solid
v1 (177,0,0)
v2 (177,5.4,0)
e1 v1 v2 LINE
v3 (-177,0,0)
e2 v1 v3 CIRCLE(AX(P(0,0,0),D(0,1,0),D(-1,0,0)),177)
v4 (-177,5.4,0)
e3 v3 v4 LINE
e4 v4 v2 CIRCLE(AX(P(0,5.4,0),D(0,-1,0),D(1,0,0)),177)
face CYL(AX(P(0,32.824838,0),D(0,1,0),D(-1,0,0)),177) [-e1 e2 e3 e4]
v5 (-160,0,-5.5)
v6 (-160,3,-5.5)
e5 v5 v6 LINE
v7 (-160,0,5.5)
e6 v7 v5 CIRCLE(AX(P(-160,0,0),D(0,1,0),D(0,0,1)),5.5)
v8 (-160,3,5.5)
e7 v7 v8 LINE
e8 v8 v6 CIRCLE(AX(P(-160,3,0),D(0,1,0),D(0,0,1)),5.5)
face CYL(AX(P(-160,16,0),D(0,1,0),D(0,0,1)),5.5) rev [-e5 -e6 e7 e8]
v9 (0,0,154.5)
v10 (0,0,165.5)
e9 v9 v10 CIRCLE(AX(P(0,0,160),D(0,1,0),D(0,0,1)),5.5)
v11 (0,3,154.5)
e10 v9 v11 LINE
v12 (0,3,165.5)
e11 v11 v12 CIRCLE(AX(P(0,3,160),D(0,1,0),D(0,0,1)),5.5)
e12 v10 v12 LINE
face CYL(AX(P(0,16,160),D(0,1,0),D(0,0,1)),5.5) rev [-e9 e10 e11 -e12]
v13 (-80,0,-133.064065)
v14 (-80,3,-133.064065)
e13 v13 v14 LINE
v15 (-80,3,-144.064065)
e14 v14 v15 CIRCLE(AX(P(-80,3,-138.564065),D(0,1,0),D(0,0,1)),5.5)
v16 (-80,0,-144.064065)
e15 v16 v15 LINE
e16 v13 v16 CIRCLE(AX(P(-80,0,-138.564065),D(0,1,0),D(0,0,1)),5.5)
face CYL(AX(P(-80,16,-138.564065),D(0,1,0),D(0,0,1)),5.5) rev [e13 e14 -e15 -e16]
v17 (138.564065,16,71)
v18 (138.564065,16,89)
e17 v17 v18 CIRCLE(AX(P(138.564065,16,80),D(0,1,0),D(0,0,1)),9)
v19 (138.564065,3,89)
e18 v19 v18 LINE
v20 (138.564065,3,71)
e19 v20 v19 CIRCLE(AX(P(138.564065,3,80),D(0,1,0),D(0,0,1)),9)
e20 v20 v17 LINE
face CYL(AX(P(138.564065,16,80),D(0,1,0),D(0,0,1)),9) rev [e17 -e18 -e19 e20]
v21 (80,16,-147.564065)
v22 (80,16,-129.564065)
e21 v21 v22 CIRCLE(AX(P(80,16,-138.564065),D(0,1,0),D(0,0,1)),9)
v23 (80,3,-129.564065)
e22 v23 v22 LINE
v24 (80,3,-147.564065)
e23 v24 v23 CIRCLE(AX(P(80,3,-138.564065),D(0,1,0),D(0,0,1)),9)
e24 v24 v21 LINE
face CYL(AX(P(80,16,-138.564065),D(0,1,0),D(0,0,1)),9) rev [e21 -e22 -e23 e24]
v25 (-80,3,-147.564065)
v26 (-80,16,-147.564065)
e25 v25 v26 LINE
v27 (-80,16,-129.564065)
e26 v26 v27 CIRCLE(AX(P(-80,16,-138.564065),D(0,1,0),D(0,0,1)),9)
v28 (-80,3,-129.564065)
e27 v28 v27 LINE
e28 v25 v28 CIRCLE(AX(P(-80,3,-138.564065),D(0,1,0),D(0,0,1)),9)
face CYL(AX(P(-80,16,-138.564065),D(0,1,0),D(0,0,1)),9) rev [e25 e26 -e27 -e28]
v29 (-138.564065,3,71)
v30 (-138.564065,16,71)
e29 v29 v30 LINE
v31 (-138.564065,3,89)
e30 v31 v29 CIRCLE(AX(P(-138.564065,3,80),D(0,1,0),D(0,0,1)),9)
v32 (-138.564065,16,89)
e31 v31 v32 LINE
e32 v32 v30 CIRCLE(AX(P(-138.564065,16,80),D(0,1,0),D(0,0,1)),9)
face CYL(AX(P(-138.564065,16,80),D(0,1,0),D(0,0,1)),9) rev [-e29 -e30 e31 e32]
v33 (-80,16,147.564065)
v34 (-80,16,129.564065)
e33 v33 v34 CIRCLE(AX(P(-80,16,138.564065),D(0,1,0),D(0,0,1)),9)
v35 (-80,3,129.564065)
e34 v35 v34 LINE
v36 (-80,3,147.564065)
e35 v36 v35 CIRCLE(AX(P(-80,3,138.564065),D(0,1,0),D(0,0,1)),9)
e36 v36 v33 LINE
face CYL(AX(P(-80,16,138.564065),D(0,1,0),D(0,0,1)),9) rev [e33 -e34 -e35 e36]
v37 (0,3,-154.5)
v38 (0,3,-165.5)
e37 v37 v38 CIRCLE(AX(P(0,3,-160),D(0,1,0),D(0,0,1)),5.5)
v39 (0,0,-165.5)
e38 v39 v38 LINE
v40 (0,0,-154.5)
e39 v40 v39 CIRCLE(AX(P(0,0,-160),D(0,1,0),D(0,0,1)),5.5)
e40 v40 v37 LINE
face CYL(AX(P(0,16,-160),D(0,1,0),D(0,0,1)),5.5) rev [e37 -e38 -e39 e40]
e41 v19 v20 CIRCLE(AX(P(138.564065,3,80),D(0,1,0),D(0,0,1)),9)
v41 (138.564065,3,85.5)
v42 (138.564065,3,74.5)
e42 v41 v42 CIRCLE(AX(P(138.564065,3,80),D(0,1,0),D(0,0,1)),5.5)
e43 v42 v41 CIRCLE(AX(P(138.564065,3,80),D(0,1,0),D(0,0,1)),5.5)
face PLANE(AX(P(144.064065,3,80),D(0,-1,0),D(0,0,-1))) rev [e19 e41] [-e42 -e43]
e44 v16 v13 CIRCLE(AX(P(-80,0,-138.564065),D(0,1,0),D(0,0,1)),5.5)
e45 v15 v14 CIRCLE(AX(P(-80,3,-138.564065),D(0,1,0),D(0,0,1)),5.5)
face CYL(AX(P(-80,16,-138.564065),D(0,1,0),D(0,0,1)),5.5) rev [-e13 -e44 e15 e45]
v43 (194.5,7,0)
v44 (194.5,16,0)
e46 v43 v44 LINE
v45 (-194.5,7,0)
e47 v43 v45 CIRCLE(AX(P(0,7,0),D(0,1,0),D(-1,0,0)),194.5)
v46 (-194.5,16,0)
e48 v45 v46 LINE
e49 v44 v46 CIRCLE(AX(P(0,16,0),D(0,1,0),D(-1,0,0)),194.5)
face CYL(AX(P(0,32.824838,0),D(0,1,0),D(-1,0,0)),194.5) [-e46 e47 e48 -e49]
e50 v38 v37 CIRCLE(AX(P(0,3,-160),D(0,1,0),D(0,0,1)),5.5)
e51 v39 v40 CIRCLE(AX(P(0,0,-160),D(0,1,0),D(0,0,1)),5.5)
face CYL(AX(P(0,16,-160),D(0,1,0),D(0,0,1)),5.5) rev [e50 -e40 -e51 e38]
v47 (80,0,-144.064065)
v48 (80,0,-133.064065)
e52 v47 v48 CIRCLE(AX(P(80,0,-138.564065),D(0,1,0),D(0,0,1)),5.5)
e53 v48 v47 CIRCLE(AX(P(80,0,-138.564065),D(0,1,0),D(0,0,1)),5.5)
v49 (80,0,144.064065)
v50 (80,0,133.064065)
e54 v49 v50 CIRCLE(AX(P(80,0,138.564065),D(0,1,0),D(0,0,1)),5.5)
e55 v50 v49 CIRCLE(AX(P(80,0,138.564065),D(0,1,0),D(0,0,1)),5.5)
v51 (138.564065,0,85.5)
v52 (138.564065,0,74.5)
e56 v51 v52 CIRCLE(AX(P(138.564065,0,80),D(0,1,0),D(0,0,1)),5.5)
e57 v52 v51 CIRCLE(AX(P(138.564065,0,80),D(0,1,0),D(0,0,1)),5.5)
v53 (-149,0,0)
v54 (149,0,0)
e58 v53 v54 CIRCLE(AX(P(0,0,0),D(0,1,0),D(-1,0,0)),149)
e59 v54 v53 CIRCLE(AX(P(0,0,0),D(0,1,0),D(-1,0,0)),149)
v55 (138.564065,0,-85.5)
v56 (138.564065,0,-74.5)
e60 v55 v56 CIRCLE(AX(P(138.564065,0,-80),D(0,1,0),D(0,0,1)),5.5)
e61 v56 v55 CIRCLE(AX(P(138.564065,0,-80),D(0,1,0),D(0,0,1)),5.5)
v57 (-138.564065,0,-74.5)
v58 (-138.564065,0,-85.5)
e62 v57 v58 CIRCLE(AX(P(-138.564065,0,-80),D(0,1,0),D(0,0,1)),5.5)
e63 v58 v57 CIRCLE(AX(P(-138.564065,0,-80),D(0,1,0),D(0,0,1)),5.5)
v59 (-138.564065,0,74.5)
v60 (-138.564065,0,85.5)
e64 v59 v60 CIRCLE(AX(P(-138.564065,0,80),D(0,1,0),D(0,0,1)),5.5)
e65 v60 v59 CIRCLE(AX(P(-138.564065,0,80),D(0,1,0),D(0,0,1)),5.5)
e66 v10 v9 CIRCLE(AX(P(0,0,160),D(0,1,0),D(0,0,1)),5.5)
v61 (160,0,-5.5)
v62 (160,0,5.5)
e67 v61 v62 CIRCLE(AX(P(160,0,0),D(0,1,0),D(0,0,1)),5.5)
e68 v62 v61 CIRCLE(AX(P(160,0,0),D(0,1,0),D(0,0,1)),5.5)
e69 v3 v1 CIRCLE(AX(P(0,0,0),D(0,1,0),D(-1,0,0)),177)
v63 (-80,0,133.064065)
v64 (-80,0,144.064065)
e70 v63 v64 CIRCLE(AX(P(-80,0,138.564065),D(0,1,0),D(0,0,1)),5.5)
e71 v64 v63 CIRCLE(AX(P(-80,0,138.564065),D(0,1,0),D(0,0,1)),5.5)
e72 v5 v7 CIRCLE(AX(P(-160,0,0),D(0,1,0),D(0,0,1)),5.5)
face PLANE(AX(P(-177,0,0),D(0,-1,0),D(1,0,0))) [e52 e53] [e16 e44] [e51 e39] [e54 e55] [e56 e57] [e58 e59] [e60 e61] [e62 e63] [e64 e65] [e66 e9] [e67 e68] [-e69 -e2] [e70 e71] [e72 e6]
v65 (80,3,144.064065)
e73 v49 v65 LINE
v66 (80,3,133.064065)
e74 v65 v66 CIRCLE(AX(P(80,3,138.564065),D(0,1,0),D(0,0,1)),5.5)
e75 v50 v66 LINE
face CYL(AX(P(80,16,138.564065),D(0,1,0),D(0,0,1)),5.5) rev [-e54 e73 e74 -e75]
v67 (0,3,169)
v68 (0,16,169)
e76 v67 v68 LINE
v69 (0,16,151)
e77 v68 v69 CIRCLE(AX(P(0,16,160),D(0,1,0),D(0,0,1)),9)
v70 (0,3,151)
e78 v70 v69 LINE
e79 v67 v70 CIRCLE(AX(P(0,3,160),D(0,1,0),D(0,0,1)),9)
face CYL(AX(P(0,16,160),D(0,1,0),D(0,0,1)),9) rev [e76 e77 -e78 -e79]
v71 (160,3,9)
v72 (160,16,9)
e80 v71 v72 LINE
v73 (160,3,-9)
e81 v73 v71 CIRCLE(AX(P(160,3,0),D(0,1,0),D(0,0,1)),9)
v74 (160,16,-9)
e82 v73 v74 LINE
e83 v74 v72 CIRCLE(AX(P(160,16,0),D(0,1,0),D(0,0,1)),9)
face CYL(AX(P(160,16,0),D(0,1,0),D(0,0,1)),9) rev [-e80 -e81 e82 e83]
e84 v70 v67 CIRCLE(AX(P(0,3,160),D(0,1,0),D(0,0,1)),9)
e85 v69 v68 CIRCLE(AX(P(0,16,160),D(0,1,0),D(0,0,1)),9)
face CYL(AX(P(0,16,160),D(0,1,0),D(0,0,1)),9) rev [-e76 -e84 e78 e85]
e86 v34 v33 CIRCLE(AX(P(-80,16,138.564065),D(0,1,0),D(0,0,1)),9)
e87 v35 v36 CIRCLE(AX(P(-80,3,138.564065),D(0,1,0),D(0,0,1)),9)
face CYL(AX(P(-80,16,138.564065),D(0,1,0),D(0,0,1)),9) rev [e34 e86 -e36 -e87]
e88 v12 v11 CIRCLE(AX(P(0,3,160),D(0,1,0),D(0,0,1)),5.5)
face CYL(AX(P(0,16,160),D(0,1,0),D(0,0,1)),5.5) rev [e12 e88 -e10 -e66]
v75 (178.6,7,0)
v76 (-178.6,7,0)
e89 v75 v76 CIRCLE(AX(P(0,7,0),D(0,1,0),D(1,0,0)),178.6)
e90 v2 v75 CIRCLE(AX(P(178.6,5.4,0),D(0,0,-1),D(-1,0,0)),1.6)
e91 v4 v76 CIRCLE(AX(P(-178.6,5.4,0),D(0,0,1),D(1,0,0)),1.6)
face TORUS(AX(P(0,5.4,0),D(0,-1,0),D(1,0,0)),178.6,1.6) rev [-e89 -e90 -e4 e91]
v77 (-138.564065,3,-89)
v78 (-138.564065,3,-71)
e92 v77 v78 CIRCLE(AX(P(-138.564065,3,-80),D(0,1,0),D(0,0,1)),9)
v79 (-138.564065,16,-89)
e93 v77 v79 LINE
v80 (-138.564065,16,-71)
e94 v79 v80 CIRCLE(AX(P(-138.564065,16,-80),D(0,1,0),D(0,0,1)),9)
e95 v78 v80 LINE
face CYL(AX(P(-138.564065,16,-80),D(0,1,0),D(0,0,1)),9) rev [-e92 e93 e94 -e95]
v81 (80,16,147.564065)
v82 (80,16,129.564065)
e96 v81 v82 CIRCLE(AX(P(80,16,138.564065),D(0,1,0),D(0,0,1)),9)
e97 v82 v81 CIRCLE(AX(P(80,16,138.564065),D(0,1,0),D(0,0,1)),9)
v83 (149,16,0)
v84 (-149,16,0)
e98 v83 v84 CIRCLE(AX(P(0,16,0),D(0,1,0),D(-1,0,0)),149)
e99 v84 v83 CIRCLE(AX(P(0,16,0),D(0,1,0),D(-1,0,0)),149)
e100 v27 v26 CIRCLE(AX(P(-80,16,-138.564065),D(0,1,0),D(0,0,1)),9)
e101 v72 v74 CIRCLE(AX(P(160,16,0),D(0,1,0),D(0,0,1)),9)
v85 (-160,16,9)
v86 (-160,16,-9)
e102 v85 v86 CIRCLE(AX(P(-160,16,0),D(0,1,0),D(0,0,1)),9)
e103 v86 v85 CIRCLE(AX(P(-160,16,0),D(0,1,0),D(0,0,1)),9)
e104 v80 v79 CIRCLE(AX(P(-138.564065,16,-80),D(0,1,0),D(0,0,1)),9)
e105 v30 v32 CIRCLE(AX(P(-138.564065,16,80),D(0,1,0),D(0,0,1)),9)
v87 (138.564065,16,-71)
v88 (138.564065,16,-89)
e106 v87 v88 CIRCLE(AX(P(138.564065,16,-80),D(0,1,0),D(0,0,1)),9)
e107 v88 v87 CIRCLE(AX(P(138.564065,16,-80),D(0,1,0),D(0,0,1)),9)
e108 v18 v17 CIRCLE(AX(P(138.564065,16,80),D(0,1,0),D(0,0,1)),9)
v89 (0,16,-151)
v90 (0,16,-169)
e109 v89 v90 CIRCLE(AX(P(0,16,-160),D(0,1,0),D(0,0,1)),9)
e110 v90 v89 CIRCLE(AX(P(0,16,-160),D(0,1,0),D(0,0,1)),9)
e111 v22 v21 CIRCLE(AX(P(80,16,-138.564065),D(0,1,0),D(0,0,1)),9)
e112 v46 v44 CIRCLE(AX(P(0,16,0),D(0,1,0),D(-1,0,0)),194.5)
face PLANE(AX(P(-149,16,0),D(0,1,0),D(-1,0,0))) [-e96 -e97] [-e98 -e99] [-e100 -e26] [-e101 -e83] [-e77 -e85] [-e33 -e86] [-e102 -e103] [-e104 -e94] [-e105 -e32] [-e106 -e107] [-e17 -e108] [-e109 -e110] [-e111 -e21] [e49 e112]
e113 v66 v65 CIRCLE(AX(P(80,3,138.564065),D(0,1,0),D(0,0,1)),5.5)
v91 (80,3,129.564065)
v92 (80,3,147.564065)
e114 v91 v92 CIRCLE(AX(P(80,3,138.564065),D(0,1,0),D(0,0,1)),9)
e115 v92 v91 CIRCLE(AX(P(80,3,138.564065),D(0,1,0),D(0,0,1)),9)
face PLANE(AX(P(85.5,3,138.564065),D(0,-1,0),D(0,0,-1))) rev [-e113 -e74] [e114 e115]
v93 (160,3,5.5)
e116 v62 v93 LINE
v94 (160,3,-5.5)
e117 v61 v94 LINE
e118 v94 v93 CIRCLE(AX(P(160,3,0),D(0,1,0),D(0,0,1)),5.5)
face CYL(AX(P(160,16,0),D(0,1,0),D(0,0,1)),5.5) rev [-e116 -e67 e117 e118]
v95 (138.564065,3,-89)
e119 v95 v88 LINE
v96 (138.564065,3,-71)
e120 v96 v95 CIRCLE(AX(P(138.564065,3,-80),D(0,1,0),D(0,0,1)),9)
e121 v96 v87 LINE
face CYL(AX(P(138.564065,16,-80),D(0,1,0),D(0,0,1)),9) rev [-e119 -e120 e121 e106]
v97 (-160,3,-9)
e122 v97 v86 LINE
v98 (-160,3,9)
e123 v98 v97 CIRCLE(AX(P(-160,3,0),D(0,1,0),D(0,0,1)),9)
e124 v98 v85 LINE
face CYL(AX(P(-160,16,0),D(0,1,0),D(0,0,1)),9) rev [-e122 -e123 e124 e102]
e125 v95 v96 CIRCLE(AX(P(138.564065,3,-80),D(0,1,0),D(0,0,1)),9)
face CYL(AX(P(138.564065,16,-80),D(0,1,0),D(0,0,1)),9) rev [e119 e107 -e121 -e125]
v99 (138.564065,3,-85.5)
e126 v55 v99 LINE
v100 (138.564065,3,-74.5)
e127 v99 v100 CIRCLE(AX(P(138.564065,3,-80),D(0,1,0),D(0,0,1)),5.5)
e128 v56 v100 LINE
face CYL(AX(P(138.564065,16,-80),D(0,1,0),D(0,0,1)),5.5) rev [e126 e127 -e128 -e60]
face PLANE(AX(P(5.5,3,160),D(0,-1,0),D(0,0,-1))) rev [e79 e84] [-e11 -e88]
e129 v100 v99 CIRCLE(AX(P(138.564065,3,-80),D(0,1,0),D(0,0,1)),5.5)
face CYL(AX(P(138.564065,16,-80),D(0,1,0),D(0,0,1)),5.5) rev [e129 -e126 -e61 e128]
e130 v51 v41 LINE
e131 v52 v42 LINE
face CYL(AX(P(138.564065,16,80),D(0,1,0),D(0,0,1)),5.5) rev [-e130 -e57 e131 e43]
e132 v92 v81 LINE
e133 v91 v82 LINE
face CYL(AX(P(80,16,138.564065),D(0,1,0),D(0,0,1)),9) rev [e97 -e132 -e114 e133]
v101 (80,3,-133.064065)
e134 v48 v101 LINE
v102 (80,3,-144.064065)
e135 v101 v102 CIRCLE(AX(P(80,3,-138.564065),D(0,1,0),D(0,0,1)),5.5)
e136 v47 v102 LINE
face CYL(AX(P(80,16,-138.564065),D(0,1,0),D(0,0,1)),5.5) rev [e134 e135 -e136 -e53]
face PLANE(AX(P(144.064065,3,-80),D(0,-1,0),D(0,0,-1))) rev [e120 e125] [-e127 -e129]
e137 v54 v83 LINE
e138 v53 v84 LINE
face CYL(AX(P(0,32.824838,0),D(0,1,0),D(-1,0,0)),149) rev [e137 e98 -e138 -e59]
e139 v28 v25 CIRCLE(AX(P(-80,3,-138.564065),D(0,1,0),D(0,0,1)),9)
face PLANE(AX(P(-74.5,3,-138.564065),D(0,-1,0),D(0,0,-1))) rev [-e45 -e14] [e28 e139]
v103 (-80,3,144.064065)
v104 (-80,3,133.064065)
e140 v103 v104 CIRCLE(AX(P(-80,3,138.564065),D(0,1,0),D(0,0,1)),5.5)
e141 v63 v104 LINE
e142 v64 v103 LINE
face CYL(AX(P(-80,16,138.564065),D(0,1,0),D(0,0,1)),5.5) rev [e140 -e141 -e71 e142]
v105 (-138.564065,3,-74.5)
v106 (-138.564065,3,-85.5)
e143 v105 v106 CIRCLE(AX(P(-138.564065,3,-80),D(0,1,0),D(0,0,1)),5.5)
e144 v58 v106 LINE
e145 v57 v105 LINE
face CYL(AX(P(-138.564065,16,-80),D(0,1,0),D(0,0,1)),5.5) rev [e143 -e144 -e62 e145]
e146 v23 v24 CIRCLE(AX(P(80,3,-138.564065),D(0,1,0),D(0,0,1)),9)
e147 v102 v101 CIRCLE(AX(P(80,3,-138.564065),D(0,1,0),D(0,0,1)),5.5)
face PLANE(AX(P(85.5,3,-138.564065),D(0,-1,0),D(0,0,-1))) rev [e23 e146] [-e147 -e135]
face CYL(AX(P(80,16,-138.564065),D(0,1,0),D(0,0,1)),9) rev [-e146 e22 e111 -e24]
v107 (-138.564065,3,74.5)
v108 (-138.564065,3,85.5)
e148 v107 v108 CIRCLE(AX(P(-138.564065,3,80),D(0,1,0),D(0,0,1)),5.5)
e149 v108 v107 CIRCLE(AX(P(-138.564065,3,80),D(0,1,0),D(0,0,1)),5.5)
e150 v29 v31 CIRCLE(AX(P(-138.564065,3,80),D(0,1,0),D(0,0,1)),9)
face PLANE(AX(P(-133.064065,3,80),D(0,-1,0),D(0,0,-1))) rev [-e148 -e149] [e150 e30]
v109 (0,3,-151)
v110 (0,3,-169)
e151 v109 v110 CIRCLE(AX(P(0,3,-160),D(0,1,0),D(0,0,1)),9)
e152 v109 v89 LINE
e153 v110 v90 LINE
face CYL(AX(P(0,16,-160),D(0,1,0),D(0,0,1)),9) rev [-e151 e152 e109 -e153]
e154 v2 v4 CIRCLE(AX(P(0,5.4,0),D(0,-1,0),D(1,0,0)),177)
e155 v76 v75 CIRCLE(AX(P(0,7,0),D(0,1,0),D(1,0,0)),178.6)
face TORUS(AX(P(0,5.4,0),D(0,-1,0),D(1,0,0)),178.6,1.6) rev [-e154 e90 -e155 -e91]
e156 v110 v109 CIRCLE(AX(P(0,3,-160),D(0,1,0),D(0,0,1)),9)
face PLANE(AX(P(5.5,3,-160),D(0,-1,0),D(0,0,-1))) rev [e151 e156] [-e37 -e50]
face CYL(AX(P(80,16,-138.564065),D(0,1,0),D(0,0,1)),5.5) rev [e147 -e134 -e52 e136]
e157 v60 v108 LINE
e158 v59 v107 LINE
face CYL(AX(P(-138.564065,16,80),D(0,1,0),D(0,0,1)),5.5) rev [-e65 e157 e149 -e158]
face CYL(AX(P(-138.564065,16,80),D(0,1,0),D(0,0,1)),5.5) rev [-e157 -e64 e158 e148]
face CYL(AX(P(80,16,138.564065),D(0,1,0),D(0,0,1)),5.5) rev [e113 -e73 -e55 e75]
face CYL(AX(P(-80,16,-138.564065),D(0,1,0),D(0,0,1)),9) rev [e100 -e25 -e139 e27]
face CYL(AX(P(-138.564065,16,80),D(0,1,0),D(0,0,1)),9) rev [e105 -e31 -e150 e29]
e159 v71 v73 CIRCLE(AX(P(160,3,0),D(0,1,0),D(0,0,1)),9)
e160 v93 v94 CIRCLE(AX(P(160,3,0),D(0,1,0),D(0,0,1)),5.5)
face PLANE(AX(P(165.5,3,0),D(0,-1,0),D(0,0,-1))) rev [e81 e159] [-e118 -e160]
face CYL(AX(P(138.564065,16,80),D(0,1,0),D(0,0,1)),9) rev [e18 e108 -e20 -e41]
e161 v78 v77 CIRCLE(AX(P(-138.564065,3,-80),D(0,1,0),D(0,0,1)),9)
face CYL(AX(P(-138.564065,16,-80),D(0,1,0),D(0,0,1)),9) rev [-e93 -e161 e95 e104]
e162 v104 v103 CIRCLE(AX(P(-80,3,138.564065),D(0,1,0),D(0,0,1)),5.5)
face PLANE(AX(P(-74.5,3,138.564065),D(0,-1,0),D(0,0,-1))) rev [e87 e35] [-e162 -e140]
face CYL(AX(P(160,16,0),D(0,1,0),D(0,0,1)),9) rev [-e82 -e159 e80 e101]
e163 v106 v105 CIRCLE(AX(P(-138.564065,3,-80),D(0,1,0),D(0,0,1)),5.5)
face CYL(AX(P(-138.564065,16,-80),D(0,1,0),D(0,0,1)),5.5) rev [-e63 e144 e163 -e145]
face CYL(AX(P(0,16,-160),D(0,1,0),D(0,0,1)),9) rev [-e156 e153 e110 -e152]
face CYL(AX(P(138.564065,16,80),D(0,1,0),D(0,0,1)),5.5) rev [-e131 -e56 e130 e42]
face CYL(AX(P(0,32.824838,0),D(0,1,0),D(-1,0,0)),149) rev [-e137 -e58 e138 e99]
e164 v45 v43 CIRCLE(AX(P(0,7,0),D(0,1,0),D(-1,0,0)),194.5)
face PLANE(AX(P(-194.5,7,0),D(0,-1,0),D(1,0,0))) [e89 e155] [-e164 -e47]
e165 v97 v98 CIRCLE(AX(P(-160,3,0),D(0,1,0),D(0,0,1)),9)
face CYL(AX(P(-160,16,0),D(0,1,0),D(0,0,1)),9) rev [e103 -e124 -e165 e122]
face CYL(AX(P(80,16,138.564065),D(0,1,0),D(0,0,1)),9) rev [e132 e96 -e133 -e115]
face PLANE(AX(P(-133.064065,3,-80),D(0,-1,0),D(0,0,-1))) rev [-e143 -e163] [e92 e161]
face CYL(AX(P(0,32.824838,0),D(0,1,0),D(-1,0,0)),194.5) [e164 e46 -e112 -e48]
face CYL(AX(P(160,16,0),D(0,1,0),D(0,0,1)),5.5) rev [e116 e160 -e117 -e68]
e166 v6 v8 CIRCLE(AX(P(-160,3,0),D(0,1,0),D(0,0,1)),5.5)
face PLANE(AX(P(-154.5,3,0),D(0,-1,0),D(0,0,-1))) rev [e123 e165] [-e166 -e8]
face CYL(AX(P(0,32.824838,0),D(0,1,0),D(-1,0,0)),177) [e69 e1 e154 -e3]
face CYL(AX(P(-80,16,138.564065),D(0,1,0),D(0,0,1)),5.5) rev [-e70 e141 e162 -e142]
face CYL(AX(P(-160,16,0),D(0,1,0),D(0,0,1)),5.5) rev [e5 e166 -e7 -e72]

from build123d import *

# Parameters (mm, degrees)
FILLET1_R                                            = 1.6
HOLE_SIZE_PER_SOCKET_HEAD_CAP_SCREW_TYPE_D           = 11
HOLE_SIZE_PER_SOCKET_HEAD_CAP_SCREW_TYPE_CBORE_D     = 18
HOLE_SIZE_PER_SOCKET_HEAD_CAP_SCREW_TYPE_CBORE_DEPTH = 13
CIRPATTERN1_COUNT                                    = 12


with BuildPart() as part:
    # Sketch1 → Revolve1 (revolve)
    with BuildSketch(Plane.XY):
        Polygon((-149, 0), (-149, 16), (-194.5, 16), (-194.5, 7), (-177, 7), (-177, 0), align=None)
    revolve(axis=Axis((0, 32.824838348, 0), (0, -1, 0)))

    # Fillet1
    fillet1_edges = [part.edges().sort_by_distance(p)[0] for p in [
        (177, 7, 0),
    ]]
    fillet(fillet1_edges, radius=FILLET1_R)

    # Hole size per socket head cap screw type1 (through all)
    with Locations(Plane(origin=(0, 16, 0), x_dir=(-1, 0, 0), z_dir=(0, 1, 0))):
        with Locations((160, 0)):
            hole_size_per_socket_head_cap_screw_type = CounterBoreHole(HOLE_SIZE_PER_SOCKET_HEAD_CAP_SCREW_TYPE_D / 2, HOLE_SIZE_PER_SOCKET_HEAD_CAP_SCREW_TYPE_CBORE_D / 2, HOLE_SIZE_PER_SOCKET_HEAD_CAP_SCREW_TYPE_CBORE_DEPTH)

    # CirPattern1: Hole size per socket head cap screw type1 ×12 about axis
    cirpattern1_axis = Axis((0, 0, 0), (0, 1, 0))
    for i in range(1, CIRPATTERN1_COUNT):
        add(hole_size_per_socket_head_cap_screw_type.rotate(cirpattern1_axis, i * 360 / CIRPATTERN1_COUNT), mode=Mode.SUBTRACT)


solid = part.part
